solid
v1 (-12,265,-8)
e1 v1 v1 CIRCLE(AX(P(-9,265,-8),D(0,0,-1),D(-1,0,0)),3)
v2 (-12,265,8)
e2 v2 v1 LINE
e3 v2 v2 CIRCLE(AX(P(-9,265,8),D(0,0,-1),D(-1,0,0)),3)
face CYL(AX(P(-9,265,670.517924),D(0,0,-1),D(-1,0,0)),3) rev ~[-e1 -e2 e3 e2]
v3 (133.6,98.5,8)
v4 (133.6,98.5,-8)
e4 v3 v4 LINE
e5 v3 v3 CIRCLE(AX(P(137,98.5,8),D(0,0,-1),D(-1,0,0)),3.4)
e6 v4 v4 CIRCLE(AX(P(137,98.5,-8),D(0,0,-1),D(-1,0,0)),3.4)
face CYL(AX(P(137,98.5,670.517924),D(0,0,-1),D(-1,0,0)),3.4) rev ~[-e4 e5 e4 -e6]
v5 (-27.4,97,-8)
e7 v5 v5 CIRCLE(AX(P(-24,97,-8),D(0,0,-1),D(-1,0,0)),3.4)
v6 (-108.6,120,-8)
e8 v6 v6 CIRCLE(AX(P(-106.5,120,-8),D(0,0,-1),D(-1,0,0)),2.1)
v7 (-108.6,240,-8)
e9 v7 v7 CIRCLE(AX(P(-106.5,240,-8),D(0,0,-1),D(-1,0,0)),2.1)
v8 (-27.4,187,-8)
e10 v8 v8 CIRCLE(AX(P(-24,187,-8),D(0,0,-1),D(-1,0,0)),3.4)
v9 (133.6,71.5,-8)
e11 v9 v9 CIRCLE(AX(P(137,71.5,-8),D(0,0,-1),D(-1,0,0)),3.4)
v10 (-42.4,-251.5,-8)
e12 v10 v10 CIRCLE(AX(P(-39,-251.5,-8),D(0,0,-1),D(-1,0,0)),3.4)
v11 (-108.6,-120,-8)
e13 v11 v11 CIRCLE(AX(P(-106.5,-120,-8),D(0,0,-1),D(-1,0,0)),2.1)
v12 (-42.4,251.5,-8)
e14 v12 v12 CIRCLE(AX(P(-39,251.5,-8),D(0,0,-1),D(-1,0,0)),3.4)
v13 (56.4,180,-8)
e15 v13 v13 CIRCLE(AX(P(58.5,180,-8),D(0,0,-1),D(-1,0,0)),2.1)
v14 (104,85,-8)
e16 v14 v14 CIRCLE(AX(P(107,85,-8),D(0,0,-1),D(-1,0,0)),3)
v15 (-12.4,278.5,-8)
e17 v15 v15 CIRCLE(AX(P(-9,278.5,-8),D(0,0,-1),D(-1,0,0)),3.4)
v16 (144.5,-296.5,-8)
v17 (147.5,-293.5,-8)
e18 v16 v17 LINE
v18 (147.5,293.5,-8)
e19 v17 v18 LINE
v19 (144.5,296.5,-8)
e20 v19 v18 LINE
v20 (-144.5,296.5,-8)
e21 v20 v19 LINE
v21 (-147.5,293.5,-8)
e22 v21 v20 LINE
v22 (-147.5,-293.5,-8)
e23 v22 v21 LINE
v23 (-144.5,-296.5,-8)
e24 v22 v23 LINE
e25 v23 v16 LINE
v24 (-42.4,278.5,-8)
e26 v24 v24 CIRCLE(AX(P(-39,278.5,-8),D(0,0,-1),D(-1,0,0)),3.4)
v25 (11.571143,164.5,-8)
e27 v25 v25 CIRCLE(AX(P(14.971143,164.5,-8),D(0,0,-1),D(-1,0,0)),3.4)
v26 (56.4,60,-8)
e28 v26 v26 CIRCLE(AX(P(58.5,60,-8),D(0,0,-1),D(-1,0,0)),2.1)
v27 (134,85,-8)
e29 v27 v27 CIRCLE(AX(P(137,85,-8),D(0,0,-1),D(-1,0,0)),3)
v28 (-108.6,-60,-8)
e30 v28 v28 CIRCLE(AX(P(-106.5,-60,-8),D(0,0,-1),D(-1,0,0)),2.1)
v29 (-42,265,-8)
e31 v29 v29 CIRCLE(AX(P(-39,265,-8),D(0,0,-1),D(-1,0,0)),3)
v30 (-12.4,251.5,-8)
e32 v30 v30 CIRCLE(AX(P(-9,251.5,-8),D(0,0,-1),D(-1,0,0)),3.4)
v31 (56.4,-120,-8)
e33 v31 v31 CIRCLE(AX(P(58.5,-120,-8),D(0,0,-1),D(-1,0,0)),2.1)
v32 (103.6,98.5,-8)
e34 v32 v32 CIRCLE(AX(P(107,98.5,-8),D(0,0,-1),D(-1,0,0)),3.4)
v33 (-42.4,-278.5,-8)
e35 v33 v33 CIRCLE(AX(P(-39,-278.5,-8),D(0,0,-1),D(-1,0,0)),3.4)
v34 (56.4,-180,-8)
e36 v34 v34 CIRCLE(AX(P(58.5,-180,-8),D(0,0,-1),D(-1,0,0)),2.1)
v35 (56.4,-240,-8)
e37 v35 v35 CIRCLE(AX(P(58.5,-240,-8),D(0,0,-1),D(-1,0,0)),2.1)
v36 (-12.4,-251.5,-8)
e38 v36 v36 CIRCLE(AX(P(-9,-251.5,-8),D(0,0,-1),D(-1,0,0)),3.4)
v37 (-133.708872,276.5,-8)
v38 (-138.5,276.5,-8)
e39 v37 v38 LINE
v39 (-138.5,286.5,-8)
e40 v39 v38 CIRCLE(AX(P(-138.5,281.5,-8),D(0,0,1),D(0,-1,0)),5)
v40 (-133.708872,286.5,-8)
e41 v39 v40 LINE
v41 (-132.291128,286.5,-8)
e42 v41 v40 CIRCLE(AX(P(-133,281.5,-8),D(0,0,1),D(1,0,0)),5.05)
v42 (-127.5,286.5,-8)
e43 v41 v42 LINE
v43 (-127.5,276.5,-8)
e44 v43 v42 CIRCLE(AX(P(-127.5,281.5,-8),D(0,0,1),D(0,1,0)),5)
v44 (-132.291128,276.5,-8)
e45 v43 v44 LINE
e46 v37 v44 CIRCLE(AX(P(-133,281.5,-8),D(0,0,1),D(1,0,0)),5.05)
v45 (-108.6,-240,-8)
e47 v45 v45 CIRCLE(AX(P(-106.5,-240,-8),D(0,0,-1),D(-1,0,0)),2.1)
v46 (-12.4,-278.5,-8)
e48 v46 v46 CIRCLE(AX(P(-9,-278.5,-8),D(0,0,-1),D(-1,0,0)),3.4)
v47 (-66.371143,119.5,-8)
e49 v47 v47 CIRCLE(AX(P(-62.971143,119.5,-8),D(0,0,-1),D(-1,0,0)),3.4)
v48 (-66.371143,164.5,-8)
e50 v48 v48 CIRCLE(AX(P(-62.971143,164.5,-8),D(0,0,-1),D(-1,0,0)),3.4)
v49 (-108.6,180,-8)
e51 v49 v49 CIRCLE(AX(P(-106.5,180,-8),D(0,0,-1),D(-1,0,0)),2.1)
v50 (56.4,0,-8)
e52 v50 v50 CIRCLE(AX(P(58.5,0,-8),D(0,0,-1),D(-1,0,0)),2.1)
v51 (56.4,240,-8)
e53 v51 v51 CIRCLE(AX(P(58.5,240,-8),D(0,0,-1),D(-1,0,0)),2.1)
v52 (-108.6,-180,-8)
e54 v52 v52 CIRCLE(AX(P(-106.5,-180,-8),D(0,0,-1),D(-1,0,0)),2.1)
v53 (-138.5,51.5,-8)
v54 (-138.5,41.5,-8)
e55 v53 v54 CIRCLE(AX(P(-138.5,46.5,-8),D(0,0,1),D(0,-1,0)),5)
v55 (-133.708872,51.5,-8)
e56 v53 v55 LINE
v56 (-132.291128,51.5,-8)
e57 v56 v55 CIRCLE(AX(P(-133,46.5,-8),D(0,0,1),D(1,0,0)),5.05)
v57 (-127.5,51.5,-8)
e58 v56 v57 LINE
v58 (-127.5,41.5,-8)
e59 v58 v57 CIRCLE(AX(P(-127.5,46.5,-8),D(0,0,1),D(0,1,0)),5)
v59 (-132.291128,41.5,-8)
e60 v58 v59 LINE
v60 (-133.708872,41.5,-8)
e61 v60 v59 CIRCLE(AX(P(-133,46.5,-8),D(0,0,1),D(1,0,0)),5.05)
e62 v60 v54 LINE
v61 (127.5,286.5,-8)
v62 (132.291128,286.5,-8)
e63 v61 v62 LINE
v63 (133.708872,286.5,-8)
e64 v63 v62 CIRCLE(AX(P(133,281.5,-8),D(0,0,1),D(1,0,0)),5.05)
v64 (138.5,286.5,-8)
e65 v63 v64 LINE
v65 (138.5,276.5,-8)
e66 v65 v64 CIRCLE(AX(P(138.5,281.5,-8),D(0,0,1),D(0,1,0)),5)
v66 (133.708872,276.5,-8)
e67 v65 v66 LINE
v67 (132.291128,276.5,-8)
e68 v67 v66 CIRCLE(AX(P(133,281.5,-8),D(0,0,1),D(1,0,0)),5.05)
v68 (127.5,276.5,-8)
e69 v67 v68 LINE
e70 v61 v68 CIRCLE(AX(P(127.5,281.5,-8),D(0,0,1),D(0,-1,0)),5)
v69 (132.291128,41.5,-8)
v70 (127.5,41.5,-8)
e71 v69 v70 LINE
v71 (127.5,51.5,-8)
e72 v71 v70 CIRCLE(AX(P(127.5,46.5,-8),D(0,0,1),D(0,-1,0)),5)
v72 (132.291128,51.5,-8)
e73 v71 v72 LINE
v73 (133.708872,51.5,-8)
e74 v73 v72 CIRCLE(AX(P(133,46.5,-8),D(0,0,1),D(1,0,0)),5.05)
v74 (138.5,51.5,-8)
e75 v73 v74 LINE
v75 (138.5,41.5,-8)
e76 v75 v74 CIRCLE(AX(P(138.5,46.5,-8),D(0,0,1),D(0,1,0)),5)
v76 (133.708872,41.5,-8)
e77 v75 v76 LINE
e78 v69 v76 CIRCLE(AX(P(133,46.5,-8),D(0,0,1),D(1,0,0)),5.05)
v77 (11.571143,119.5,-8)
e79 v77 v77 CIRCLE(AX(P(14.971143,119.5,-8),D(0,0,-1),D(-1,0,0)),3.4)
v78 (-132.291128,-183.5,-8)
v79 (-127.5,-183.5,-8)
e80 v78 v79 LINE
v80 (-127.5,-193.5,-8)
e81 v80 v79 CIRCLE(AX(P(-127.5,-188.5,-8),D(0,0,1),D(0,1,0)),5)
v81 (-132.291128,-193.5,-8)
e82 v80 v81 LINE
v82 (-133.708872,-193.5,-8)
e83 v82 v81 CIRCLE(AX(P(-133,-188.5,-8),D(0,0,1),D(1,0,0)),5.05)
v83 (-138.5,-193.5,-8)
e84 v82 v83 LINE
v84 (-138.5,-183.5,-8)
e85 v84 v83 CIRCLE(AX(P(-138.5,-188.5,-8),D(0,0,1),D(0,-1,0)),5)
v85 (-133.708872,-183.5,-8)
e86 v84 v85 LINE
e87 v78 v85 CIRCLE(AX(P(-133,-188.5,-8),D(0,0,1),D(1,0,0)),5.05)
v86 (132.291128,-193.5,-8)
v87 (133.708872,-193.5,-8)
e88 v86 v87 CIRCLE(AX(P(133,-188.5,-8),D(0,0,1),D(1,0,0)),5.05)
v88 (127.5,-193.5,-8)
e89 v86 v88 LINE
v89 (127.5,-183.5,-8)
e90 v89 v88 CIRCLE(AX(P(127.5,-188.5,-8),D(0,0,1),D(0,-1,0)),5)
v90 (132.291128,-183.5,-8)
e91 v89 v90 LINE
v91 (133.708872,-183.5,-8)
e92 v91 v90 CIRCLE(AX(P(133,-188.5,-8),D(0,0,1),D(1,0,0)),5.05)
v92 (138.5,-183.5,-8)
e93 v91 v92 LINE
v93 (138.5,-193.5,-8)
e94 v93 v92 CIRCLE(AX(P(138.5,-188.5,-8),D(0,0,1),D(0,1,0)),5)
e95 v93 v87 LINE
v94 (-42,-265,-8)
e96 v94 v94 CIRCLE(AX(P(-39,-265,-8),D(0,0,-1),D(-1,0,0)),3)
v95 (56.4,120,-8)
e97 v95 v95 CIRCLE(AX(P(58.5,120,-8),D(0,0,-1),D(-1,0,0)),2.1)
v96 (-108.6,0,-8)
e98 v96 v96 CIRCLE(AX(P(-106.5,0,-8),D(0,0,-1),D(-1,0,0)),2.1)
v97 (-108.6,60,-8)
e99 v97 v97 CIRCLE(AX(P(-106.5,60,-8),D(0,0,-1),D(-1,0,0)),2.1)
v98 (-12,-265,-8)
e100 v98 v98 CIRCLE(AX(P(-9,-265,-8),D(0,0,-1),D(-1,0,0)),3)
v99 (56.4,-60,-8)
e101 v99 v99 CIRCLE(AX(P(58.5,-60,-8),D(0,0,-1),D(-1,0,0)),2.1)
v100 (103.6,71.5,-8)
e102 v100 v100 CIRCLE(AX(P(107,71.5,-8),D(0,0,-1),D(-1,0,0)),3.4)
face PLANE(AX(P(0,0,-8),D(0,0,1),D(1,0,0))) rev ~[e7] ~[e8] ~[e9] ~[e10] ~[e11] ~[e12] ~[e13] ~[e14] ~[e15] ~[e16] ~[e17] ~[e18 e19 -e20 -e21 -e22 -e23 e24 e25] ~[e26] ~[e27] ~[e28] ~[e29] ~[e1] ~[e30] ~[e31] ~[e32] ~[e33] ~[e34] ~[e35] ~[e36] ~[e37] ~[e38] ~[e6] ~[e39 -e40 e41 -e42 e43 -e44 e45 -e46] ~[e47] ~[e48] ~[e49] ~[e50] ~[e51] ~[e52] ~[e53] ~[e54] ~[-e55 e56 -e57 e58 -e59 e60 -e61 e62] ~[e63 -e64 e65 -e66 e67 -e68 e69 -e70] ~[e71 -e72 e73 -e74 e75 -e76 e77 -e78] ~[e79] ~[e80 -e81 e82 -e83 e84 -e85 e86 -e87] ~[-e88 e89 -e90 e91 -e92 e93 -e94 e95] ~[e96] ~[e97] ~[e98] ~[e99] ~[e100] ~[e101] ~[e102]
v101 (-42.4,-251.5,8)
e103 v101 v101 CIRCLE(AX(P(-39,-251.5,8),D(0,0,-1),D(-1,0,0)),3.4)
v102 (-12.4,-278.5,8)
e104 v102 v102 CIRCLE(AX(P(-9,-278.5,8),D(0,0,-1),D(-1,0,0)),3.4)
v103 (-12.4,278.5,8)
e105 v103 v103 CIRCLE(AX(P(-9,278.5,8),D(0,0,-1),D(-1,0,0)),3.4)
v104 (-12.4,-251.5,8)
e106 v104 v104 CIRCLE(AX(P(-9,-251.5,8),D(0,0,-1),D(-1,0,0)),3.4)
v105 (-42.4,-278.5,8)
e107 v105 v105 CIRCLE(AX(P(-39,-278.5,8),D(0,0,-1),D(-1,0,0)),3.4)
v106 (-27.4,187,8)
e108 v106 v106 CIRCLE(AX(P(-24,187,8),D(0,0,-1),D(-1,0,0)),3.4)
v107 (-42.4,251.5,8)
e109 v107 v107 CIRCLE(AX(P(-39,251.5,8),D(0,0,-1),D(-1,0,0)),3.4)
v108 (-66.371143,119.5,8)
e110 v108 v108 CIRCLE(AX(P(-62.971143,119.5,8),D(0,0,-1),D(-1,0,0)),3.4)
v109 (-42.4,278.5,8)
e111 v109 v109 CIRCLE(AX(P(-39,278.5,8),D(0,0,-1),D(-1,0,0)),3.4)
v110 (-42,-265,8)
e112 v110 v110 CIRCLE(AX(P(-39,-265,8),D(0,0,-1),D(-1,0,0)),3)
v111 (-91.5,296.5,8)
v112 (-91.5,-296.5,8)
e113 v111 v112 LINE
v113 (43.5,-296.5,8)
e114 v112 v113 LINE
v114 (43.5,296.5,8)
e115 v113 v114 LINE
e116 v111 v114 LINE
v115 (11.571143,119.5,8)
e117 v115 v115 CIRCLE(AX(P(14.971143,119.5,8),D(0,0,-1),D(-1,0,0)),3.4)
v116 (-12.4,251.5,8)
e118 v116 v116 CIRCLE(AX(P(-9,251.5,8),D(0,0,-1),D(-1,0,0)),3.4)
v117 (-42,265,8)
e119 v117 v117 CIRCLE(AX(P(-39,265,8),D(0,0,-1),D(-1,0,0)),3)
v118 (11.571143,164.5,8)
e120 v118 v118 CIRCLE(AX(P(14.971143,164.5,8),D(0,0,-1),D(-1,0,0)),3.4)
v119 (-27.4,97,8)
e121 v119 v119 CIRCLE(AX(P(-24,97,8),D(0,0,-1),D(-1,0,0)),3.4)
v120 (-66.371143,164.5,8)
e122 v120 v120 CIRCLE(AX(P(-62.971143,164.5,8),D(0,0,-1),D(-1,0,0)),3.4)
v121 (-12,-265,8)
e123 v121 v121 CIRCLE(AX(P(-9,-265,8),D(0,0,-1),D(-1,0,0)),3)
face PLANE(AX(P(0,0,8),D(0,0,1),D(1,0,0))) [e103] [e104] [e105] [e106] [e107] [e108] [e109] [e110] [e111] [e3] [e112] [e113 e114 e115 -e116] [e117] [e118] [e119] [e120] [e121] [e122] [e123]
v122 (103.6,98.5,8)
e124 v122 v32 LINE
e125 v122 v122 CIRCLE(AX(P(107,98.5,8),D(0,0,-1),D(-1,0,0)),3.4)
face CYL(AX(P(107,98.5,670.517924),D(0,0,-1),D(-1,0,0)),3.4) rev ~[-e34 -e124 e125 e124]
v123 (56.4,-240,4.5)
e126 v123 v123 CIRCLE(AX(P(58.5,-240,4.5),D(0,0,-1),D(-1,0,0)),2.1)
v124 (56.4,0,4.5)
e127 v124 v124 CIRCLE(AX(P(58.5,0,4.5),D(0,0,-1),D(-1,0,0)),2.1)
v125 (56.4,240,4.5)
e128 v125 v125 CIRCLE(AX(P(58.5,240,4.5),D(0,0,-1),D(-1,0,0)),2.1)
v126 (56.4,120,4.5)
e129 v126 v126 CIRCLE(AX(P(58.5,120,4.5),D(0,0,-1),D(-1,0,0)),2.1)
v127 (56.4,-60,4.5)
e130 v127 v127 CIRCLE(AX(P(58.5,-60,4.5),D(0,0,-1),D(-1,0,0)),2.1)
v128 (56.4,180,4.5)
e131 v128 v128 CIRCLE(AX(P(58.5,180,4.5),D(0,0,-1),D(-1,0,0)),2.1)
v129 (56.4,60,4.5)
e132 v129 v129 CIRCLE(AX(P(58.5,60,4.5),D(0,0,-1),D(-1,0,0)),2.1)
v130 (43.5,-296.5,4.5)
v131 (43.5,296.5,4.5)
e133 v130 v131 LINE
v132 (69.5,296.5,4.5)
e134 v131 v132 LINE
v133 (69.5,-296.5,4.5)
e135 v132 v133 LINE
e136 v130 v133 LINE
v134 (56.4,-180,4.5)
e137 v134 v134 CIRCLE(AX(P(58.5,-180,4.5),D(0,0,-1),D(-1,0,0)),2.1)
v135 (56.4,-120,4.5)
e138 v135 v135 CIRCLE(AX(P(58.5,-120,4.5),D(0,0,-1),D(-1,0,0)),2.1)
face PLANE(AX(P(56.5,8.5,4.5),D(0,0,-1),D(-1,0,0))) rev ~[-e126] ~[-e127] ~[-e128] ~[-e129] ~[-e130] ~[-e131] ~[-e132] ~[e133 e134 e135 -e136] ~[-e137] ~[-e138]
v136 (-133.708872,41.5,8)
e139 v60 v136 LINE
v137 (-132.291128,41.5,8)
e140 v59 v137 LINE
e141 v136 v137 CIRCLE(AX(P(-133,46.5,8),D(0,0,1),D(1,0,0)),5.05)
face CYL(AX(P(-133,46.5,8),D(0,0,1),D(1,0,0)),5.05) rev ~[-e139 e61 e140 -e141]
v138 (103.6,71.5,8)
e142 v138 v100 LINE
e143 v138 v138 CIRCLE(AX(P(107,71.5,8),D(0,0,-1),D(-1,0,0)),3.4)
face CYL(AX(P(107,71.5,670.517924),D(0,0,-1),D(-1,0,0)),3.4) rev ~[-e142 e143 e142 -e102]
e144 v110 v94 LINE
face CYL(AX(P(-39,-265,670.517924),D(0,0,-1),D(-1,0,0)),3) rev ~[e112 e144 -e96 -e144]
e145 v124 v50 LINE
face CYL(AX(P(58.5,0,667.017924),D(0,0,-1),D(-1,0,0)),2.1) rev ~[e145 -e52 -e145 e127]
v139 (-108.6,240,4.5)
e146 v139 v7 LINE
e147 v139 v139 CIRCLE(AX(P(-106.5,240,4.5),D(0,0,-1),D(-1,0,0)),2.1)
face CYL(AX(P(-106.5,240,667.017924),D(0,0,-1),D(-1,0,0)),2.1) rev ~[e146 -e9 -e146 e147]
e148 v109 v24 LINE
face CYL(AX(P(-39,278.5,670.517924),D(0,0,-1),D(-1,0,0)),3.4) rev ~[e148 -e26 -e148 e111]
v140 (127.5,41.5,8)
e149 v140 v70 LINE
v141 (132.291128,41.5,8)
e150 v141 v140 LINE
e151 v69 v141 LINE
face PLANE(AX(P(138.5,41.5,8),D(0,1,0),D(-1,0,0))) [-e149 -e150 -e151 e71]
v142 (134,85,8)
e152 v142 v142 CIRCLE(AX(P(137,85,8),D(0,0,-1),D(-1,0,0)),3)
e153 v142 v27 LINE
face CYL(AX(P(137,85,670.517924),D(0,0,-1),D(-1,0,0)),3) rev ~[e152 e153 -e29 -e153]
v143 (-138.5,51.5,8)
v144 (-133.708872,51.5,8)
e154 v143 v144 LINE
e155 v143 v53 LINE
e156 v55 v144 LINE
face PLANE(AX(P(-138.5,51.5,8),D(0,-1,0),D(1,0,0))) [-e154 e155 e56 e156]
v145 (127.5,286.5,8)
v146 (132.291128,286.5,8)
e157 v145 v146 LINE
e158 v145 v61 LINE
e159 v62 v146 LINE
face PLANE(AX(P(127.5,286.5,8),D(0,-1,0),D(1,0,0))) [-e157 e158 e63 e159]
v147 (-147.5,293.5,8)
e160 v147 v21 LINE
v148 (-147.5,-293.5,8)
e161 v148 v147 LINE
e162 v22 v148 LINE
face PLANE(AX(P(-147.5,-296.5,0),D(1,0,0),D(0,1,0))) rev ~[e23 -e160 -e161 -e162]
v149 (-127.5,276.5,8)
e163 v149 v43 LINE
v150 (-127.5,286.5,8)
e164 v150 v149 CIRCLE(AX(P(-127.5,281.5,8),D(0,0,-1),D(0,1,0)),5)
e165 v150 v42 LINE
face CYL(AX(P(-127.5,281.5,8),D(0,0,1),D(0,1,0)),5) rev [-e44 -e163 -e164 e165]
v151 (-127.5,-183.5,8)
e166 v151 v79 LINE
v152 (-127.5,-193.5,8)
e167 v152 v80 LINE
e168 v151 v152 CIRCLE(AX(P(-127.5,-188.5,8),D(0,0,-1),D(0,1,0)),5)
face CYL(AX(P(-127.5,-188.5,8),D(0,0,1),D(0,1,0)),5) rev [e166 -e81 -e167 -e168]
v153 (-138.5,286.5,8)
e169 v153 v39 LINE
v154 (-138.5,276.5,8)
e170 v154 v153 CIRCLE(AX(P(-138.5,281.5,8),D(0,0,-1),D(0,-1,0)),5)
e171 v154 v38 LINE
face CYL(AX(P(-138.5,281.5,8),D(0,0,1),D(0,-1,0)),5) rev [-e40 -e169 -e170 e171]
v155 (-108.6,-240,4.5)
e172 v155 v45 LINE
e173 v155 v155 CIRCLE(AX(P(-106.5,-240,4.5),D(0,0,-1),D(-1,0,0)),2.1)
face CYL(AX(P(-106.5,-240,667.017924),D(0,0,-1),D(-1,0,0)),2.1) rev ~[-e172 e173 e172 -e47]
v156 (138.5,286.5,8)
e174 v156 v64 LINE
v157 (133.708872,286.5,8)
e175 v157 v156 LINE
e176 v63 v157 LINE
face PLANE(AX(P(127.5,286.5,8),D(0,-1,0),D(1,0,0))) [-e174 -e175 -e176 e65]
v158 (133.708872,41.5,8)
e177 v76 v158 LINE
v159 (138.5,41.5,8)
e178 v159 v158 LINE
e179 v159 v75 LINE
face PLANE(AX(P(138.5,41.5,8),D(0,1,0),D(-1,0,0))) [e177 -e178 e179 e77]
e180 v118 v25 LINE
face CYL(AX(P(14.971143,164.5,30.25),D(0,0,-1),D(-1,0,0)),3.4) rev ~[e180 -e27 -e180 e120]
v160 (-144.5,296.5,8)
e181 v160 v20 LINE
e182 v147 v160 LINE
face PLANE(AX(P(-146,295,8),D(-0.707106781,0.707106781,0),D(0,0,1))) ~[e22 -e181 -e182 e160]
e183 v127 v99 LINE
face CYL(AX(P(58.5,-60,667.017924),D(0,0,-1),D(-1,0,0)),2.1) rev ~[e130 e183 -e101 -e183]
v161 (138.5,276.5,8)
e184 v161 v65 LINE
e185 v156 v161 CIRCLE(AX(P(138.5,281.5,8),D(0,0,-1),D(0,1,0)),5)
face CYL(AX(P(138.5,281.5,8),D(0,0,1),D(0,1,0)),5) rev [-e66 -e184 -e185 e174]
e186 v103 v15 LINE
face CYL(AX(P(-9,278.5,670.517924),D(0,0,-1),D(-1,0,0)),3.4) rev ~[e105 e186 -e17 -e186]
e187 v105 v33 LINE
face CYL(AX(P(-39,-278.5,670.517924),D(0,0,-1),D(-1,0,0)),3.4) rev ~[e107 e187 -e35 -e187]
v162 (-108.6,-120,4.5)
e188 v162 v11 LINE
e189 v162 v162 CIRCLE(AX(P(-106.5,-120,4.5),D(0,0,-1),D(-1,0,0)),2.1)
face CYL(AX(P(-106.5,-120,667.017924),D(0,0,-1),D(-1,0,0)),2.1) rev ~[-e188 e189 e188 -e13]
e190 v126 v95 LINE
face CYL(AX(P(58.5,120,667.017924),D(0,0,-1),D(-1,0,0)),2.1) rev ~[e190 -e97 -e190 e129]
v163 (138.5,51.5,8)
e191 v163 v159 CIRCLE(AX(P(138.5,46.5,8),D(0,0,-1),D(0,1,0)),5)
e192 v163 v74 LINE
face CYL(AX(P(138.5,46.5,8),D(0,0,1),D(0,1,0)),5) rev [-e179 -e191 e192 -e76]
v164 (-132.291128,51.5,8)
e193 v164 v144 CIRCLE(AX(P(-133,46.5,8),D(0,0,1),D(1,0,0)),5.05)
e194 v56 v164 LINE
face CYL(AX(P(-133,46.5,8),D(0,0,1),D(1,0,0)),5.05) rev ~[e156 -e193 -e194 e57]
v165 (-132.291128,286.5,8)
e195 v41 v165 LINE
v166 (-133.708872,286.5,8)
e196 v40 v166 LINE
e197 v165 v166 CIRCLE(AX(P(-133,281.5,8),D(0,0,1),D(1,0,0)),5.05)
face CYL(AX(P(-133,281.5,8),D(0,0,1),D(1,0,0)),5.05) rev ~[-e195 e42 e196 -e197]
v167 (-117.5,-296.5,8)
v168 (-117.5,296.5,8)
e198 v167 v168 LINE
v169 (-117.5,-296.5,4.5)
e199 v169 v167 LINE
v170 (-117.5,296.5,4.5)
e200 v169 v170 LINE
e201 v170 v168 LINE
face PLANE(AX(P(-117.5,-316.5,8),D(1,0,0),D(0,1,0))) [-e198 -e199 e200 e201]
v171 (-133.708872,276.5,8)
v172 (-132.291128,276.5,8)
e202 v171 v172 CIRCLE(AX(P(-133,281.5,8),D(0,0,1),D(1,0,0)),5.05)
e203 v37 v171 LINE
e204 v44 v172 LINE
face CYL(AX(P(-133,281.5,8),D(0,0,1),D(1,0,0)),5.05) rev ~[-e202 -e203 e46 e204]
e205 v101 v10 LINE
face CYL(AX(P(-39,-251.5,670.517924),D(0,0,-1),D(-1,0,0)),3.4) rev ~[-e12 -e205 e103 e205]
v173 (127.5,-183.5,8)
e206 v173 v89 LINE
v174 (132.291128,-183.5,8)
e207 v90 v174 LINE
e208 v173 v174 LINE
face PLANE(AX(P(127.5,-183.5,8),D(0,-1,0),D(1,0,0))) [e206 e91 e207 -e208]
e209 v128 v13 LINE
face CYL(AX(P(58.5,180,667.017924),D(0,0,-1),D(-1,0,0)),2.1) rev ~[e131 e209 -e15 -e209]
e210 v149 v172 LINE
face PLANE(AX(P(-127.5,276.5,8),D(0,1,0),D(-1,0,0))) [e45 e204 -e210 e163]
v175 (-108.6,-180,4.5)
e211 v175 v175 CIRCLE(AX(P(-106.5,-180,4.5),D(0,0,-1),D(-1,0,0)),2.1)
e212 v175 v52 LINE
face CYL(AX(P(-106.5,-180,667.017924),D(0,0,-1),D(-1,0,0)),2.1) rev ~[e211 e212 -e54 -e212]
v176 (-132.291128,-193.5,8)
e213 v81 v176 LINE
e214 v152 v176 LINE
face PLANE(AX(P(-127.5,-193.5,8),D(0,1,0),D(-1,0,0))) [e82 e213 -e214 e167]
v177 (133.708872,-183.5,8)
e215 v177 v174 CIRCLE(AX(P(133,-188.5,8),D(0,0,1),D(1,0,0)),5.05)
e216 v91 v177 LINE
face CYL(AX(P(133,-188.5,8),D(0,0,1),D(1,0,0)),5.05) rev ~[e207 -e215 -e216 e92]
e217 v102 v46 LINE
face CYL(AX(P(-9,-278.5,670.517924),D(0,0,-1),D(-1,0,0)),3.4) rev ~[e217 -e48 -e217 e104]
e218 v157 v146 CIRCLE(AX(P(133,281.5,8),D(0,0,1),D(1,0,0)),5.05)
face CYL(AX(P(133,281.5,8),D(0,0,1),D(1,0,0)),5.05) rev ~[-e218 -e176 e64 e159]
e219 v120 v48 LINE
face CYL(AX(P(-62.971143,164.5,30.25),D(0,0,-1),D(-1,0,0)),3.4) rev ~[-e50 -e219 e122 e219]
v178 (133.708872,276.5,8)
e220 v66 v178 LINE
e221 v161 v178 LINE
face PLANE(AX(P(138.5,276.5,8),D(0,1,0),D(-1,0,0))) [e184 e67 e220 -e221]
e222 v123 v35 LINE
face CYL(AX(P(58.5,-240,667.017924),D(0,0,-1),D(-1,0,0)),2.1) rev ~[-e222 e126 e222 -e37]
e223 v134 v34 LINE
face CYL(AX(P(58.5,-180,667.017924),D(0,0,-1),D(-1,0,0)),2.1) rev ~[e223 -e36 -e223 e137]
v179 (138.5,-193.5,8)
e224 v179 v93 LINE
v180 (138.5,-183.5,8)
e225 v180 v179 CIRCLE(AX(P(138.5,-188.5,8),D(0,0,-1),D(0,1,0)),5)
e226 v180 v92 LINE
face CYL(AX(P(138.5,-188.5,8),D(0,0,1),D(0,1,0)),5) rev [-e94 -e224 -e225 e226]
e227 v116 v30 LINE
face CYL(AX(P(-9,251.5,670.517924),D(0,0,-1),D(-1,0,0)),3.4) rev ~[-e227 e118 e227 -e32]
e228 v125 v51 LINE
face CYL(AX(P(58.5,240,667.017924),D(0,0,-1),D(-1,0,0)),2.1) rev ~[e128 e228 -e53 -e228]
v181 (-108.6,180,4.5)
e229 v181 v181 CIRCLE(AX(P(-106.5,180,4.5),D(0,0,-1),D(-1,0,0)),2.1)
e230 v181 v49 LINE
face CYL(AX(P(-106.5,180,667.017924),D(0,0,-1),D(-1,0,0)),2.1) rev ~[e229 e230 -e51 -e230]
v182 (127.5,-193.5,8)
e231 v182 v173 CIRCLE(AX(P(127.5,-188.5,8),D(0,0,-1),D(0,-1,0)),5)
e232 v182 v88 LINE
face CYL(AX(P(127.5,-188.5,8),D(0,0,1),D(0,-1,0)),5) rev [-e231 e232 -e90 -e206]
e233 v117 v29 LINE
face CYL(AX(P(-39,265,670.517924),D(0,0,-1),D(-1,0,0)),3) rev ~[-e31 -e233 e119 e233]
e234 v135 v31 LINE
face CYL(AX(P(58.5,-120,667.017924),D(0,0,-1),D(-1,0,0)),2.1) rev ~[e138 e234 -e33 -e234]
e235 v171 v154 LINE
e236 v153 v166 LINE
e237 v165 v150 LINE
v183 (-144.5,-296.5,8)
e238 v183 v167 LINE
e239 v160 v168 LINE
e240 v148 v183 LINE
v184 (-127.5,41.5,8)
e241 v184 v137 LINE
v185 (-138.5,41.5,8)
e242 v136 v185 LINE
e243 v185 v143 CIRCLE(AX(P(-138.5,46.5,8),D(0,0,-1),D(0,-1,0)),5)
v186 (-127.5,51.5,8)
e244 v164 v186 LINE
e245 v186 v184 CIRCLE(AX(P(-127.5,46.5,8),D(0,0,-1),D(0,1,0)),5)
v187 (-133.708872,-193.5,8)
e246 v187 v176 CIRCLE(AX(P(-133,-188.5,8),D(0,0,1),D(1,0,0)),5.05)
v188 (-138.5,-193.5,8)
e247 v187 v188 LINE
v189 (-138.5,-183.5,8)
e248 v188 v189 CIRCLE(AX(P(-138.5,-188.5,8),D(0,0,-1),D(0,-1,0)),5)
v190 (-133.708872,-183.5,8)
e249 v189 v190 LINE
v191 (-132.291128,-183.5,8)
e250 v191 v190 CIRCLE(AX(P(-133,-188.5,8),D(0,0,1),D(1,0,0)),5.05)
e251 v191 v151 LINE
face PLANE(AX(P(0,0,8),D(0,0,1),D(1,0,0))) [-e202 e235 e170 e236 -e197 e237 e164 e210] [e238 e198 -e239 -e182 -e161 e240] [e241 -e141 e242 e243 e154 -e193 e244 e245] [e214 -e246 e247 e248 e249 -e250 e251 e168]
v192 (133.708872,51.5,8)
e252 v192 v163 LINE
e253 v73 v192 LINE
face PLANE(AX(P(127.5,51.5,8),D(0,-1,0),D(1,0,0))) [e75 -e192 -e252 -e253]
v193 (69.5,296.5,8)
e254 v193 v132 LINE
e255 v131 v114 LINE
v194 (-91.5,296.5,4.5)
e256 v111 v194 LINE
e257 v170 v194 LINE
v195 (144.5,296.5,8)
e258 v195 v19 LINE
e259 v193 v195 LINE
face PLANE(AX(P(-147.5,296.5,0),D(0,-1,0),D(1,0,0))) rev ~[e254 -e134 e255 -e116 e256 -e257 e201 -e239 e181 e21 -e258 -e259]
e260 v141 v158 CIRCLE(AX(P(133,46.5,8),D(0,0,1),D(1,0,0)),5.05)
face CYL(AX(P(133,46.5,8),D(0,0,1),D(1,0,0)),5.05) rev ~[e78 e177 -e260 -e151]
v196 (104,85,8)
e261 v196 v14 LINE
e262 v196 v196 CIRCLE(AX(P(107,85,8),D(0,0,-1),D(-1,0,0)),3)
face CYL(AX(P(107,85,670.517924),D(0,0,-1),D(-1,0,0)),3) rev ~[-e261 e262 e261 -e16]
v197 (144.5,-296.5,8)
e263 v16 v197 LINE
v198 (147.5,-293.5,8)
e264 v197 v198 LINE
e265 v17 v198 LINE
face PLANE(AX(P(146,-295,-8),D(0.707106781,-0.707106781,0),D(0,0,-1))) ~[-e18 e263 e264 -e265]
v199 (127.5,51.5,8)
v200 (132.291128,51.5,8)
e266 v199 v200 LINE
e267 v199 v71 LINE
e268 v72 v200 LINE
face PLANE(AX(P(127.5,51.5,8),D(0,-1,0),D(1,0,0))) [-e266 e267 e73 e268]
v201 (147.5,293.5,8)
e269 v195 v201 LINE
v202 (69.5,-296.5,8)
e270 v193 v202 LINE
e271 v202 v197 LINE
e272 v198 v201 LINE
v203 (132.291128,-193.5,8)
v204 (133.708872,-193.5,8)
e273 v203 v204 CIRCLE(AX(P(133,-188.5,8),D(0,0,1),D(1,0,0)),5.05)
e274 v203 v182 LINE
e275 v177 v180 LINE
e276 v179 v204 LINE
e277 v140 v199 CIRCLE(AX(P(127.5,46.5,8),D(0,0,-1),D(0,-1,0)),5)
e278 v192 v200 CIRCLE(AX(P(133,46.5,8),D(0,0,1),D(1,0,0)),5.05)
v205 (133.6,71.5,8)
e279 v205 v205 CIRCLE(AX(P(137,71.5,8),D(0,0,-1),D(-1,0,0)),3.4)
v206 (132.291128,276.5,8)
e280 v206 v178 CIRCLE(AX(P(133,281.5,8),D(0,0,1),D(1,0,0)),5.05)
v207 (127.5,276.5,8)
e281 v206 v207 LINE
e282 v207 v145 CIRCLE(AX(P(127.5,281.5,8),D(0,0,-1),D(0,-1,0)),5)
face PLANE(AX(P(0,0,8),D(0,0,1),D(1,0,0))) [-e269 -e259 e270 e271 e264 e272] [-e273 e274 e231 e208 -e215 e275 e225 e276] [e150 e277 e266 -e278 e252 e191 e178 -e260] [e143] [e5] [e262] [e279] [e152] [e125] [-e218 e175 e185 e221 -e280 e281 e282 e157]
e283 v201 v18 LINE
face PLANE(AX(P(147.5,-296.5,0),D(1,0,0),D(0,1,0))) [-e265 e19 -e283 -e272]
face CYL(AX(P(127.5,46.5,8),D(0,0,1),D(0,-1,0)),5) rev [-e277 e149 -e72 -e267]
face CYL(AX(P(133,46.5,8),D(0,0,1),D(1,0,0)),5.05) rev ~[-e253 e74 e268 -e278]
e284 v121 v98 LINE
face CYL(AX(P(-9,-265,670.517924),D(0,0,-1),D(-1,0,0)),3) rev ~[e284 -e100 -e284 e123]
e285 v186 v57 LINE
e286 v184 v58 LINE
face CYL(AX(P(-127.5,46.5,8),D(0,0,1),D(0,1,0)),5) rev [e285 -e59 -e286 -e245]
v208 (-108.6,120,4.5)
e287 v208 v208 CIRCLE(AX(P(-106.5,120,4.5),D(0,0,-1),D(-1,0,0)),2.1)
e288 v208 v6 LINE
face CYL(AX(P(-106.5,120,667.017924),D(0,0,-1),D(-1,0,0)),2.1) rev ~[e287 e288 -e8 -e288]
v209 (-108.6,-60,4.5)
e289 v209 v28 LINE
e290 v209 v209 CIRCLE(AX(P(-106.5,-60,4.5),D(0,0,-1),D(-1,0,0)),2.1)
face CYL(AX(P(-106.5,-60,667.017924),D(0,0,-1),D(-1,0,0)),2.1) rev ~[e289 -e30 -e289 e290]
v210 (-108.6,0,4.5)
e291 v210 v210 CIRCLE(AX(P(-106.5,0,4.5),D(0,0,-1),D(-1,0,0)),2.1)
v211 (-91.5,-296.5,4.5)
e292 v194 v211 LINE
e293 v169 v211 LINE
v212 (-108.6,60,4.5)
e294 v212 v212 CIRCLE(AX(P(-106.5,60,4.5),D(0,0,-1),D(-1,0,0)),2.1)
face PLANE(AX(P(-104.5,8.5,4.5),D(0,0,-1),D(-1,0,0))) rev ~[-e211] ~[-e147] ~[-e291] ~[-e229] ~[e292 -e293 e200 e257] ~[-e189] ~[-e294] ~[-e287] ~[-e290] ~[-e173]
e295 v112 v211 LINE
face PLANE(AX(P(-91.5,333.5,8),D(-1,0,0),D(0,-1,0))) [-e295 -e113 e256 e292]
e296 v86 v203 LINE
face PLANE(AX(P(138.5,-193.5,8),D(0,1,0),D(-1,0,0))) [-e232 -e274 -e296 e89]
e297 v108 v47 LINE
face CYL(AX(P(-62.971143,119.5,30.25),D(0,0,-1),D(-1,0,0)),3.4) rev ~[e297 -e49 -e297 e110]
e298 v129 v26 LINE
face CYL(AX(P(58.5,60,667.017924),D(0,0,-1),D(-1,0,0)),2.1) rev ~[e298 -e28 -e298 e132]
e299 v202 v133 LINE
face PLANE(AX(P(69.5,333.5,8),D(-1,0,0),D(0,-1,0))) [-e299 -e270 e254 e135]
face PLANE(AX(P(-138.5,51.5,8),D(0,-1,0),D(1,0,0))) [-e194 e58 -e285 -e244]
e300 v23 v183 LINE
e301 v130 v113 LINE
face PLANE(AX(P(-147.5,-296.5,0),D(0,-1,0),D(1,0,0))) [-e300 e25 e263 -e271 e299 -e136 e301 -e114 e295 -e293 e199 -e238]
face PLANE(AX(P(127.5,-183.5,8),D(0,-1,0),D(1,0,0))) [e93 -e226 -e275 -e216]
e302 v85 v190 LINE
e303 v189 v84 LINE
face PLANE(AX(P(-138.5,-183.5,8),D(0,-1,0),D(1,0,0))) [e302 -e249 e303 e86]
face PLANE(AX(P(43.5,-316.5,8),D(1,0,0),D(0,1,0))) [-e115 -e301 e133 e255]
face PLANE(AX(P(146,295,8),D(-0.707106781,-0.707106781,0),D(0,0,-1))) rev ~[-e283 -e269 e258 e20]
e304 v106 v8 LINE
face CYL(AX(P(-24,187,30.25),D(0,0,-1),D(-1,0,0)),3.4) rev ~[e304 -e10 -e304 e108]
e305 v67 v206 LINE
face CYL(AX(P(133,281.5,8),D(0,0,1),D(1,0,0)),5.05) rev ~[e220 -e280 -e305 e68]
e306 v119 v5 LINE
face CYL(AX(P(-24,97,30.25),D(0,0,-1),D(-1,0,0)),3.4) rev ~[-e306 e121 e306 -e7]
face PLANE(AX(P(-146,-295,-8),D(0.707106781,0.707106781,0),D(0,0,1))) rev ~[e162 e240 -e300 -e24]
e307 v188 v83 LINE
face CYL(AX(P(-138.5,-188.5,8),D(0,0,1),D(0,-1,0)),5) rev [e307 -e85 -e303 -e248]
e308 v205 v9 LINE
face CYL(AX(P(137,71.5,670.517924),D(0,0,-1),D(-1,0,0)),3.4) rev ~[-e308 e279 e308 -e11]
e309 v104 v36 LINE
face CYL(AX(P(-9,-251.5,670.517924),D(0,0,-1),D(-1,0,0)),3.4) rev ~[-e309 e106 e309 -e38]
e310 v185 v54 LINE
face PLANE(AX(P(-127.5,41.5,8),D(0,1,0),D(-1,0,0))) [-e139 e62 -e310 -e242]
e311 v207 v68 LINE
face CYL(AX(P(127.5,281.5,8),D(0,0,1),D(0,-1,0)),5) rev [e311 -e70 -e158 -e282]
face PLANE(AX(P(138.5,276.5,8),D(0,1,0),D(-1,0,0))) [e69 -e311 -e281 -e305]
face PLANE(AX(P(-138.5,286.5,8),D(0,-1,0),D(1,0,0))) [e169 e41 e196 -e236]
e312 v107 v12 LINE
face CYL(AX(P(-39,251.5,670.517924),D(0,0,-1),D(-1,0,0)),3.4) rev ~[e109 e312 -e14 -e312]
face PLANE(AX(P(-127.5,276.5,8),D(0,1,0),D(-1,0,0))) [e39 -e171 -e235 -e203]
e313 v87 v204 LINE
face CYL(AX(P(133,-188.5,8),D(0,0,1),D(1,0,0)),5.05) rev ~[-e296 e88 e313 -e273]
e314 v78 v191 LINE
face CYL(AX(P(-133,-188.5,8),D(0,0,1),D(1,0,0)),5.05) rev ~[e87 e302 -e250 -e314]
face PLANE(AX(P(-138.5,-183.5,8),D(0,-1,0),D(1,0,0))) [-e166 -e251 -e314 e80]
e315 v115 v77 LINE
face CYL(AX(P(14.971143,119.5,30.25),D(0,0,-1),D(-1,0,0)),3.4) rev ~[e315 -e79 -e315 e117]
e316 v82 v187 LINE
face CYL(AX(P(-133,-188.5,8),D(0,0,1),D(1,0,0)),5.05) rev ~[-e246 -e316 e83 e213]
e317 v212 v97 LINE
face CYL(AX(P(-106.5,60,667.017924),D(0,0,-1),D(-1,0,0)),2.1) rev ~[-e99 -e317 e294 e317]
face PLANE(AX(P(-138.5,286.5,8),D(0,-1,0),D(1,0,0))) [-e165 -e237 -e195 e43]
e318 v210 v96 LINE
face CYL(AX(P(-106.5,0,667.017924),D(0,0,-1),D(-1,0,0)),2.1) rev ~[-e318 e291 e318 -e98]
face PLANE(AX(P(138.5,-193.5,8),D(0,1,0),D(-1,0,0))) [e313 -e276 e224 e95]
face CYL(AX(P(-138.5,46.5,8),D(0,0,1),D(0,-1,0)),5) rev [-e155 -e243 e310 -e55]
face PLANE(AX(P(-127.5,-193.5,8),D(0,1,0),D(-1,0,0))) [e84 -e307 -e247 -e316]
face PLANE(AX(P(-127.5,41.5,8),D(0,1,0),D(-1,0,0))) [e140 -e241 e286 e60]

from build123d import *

# Parameters (mm, degrees)
SKETCH1_W                    = 295
SKETCH1_H                    = 593
EXTRUDE1_DEPTH               = 8
CUT_EXTRUDE1_DEPTH           = 3.5
CHAMFER1_SIZE                = 3
CUT_EXTRUDE2_DEPTH           = 30
M8_TAPPED_HOLE1_D            = 6.8
M8_TAPPED_HOLE1_DEPTH        = 22.25
M8_TAPPED_HOLE1_TIP          = 2.042926105
SKETCH6_R                    = 5.05
CUT_EXTRUDE3_DEPTH           = 20
M8_TAPPED_HOLE2_D            = 6.8
SIZE_MM_BLIND_DOWEL_HOLE_1_D = 6
M8_TAPPED_HOLE3_D            = 6.8
SIZE_MM_BLIND_DOWEL_HOLE_2_D = 6
M5_TAPPED_HOLE1_D            = 4.2


with BuildPart() as part:
    # Sketch1 → Extrude1 (new, symmetric)
    with BuildSketch(Plane.XY):
        Rectangle(SKETCH1_W, SKETCH1_H)
    extrude(amount=EXTRUDE1_DEPTH, both=True)

    # 草图1 → Cut-Extrude1 (cut)
    with BuildSketch(Plane.XY.offset(8)):
        with BuildLine():
            Line((-91.5, 333.5), (-91.5, -316.5))
            ThreePointArc((-91.5, -316.5), (-104.5, -329.5), (-117.5, -316.5))
            Line((-117.5, -316.5), (-117.5, 333.5))
            ThreePointArc((-117.5, 333.5), (-104.5, 346.5), (-91.5, 333.5))
        make_face()
        with BuildLine():
            Line((69.5, 333.5), (69.5, -316.5))
            ThreePointArc((69.5, -316.5), (56.5, -329.5), (43.5, -316.5))
            Line((43.5, -316.5), (43.5, 333.5))
            ThreePointArc((43.5, 333.5), (56.5, 346.5), (69.5, 333.5))
        make_face()
    extrude(amount=-CUT_EXTRUDE1_DEPTH, mode=Mode.SUBTRACT)

    # Chamfer1
    chamfer1_edges = [part.edges().sort_by_distance(p)[0] for p in [
        (-147.5, 296.5, 0),
        (147.5, 296.5, 0),
        (147.5, -296.5, 0),
        (-147.5, -296.5, 0),
    ]]
    chamfer(chamfer1_edges, length=CHAMFER1_SIZE)

    # Sketch2 → Cut-Extrude2 (cut)
    with BuildSketch(Plane.XY.offset(8)):
        with BuildLine():
            Line((138.5, 276.5), (127.5, 276.5))
            ThreePointArc((127.5, 276.5), (122.5, 281.5), (127.5, 286.5))
            Line((127.5, 286.5), (138.5, 286.5))
            ThreePointArc((138.5, 286.5), (143.5, 281.5), (138.5, 276.5))
        make_face()
        with BuildLine():
            Line((-127.5, 276.5), (-138.5, 276.5))
            ThreePointArc((-138.5, 276.5), (-143.5, 281.5), (-138.5, 286.5))
            Line((-138.5, 286.5), (-127.5, 286.5))
            ThreePointArc((-127.5, 286.5), (-122.5, 281.5), (-127.5, 276.5))
        make_face()
        with BuildLine():
            Line((-127.5, -193.5), (-138.5, -193.5))
            ThreePointArc((-138.5, -193.5), (-143.5, -188.5), (-138.5, -183.5))
            Line((-138.5, -183.5), (-127.5, -183.5))
            ThreePointArc((-127.5, -183.5), (-122.5, -188.5), (-127.5, -193.5))
        make_face()
        with BuildLine():
            Line((-127.5, 41.5), (-138.5, 41.5))
            ThreePointArc((-138.5, 41.5), (-143.5, 46.5), (-138.5, 51.5))
            Line((-138.5, 51.5), (-127.5, 51.5))
            ThreePointArc((-127.5, 51.5), (-122.5, 46.5), (-127.5, 41.5))
        make_face()
        with BuildLine():
            Line((138.5, -193.5), (127.5, -193.5))
            ThreePointArc((127.5, -193.5), (122.5, -188.5), (127.5, -183.5))
            Line((127.5, -183.5), (138.5, -183.5))
            ThreePointArc((138.5, -183.5), (143.5, -188.5), (138.5, -193.5))
        make_face()
        with BuildLine():
            Line((138.5, 41.5), (127.5, 41.5))
            ThreePointArc((127.5, 41.5), (122.5, 46.5), (127.5, 51.5))
            Line((127.5, 51.5), (138.5, 51.5))
            ThreePointArc((138.5, 51.5), (143.5, 46.5), (138.5, 41.5))
        make_face()
    extrude(amount=-CUT_EXTRUDE2_DEPTH, mode=Mode.SUBTRACT)

    # M8 Tapped Hole1
    with Locations(Plane.XY.offset(8)):
        with Locations((14.97114317, 164.5), (14.97114317, 119.5), (-24, 97), (-62.97114317, 119.5), (-62.97114317, 164.5), (-24, 187)):
            Hole(M8_TAPPED_HOLE1_D / 2, depth=M8_TAPPED_HOLE1_DEPTH)
            with Locations((0, 0, -(M8_TAPPED_HOLE1_DEPTH + M8_TAPPED_HOLE1_TIP / 2))):  # 118° drill point
                Cone(0, M8_TAPPED_HOLE1_D / 2, M8_TAPPED_HOLE1_TIP, mode=Mode.SUBTRACT)

    # Sketch6 → Cut-Extrude3 (cut)
    with BuildSketch(Plane.XY.offset(8)):
        with Locations((-133, 281.5)):
            Circle(SKETCH6_R)
        with Locations((133, 281.5)):
            Circle(SKETCH6_R)
        with Locations((-133, 46.5)):
            Circle(SKETCH6_R)
        with Locations((133, 46.5)):
            Circle(SKETCH6_R)
        with Locations((-133, -188.5)):
            Circle(SKETCH6_R)
        with Locations((133, -188.5)):
            Circle(SKETCH6_R)
    extrude(amount=-CUT_EXTRUDE3_DEPTH, mode=Mode.SUBTRACT)

    # M8 Tapped Hole2 (through all)
    with Locations(Plane.XY.offset(8)):
        with Locations((107, 71.5), (137, 71.5), (137, 98.5), (107, 98.5)):
            Hole(M8_TAPPED_HOLE2_D / 2)

    # Size mm blind dowel hole 1 (through all)
    with Locations(Plane.XY.offset(8)):
        with Locations((107, 85), (137, 85)):
            Hole(SIZE_MM_BLIND_DOWEL_HOLE_1_D / 2)

    # M8 Tapped Hole3 (through all)
    with Locations(Plane.XY.offset(8)):
        with Locations((-9, 278.5), (-9, 251.5), (-39, 278.5), (-39, 251.5), (-9, -251.5), (-9, -278.5), (-39, -278.5), (-39, -251.5)):
            Hole(M8_TAPPED_HOLE3_D / 2)

    # Size mm blind dowel hole 2 (through all)
    with Locations(Plane.XY.offset(8)):
        with Locations((-9, 265), (-39, 265), (-9, -265), (-39, -265)):
            Hole(SIZE_MM_BLIND_DOWEL_HOLE_2_D / 2)

    # M5 Tapped Hole1 (through all)
    with Locations(Plane.XY.offset(4.5)):
        with Locations((58.5, 240), (58.5, 180), (58.5, 120), (58.5, 60), (58.5, 0), (58.5, -60), (58.5, -120), (58.5, -180), (58.5, -240), (-106.5, -240), (-106.5, -180), (-106.5, -120), (-106.5, -60), (-106.5, 0), (-106.5, 60), (-106.5, 120), (-106.5, 180), (-106.5, 240)):
            Hole(M5_TAPPED_HOLE1_D / 2)


solid = part.part
